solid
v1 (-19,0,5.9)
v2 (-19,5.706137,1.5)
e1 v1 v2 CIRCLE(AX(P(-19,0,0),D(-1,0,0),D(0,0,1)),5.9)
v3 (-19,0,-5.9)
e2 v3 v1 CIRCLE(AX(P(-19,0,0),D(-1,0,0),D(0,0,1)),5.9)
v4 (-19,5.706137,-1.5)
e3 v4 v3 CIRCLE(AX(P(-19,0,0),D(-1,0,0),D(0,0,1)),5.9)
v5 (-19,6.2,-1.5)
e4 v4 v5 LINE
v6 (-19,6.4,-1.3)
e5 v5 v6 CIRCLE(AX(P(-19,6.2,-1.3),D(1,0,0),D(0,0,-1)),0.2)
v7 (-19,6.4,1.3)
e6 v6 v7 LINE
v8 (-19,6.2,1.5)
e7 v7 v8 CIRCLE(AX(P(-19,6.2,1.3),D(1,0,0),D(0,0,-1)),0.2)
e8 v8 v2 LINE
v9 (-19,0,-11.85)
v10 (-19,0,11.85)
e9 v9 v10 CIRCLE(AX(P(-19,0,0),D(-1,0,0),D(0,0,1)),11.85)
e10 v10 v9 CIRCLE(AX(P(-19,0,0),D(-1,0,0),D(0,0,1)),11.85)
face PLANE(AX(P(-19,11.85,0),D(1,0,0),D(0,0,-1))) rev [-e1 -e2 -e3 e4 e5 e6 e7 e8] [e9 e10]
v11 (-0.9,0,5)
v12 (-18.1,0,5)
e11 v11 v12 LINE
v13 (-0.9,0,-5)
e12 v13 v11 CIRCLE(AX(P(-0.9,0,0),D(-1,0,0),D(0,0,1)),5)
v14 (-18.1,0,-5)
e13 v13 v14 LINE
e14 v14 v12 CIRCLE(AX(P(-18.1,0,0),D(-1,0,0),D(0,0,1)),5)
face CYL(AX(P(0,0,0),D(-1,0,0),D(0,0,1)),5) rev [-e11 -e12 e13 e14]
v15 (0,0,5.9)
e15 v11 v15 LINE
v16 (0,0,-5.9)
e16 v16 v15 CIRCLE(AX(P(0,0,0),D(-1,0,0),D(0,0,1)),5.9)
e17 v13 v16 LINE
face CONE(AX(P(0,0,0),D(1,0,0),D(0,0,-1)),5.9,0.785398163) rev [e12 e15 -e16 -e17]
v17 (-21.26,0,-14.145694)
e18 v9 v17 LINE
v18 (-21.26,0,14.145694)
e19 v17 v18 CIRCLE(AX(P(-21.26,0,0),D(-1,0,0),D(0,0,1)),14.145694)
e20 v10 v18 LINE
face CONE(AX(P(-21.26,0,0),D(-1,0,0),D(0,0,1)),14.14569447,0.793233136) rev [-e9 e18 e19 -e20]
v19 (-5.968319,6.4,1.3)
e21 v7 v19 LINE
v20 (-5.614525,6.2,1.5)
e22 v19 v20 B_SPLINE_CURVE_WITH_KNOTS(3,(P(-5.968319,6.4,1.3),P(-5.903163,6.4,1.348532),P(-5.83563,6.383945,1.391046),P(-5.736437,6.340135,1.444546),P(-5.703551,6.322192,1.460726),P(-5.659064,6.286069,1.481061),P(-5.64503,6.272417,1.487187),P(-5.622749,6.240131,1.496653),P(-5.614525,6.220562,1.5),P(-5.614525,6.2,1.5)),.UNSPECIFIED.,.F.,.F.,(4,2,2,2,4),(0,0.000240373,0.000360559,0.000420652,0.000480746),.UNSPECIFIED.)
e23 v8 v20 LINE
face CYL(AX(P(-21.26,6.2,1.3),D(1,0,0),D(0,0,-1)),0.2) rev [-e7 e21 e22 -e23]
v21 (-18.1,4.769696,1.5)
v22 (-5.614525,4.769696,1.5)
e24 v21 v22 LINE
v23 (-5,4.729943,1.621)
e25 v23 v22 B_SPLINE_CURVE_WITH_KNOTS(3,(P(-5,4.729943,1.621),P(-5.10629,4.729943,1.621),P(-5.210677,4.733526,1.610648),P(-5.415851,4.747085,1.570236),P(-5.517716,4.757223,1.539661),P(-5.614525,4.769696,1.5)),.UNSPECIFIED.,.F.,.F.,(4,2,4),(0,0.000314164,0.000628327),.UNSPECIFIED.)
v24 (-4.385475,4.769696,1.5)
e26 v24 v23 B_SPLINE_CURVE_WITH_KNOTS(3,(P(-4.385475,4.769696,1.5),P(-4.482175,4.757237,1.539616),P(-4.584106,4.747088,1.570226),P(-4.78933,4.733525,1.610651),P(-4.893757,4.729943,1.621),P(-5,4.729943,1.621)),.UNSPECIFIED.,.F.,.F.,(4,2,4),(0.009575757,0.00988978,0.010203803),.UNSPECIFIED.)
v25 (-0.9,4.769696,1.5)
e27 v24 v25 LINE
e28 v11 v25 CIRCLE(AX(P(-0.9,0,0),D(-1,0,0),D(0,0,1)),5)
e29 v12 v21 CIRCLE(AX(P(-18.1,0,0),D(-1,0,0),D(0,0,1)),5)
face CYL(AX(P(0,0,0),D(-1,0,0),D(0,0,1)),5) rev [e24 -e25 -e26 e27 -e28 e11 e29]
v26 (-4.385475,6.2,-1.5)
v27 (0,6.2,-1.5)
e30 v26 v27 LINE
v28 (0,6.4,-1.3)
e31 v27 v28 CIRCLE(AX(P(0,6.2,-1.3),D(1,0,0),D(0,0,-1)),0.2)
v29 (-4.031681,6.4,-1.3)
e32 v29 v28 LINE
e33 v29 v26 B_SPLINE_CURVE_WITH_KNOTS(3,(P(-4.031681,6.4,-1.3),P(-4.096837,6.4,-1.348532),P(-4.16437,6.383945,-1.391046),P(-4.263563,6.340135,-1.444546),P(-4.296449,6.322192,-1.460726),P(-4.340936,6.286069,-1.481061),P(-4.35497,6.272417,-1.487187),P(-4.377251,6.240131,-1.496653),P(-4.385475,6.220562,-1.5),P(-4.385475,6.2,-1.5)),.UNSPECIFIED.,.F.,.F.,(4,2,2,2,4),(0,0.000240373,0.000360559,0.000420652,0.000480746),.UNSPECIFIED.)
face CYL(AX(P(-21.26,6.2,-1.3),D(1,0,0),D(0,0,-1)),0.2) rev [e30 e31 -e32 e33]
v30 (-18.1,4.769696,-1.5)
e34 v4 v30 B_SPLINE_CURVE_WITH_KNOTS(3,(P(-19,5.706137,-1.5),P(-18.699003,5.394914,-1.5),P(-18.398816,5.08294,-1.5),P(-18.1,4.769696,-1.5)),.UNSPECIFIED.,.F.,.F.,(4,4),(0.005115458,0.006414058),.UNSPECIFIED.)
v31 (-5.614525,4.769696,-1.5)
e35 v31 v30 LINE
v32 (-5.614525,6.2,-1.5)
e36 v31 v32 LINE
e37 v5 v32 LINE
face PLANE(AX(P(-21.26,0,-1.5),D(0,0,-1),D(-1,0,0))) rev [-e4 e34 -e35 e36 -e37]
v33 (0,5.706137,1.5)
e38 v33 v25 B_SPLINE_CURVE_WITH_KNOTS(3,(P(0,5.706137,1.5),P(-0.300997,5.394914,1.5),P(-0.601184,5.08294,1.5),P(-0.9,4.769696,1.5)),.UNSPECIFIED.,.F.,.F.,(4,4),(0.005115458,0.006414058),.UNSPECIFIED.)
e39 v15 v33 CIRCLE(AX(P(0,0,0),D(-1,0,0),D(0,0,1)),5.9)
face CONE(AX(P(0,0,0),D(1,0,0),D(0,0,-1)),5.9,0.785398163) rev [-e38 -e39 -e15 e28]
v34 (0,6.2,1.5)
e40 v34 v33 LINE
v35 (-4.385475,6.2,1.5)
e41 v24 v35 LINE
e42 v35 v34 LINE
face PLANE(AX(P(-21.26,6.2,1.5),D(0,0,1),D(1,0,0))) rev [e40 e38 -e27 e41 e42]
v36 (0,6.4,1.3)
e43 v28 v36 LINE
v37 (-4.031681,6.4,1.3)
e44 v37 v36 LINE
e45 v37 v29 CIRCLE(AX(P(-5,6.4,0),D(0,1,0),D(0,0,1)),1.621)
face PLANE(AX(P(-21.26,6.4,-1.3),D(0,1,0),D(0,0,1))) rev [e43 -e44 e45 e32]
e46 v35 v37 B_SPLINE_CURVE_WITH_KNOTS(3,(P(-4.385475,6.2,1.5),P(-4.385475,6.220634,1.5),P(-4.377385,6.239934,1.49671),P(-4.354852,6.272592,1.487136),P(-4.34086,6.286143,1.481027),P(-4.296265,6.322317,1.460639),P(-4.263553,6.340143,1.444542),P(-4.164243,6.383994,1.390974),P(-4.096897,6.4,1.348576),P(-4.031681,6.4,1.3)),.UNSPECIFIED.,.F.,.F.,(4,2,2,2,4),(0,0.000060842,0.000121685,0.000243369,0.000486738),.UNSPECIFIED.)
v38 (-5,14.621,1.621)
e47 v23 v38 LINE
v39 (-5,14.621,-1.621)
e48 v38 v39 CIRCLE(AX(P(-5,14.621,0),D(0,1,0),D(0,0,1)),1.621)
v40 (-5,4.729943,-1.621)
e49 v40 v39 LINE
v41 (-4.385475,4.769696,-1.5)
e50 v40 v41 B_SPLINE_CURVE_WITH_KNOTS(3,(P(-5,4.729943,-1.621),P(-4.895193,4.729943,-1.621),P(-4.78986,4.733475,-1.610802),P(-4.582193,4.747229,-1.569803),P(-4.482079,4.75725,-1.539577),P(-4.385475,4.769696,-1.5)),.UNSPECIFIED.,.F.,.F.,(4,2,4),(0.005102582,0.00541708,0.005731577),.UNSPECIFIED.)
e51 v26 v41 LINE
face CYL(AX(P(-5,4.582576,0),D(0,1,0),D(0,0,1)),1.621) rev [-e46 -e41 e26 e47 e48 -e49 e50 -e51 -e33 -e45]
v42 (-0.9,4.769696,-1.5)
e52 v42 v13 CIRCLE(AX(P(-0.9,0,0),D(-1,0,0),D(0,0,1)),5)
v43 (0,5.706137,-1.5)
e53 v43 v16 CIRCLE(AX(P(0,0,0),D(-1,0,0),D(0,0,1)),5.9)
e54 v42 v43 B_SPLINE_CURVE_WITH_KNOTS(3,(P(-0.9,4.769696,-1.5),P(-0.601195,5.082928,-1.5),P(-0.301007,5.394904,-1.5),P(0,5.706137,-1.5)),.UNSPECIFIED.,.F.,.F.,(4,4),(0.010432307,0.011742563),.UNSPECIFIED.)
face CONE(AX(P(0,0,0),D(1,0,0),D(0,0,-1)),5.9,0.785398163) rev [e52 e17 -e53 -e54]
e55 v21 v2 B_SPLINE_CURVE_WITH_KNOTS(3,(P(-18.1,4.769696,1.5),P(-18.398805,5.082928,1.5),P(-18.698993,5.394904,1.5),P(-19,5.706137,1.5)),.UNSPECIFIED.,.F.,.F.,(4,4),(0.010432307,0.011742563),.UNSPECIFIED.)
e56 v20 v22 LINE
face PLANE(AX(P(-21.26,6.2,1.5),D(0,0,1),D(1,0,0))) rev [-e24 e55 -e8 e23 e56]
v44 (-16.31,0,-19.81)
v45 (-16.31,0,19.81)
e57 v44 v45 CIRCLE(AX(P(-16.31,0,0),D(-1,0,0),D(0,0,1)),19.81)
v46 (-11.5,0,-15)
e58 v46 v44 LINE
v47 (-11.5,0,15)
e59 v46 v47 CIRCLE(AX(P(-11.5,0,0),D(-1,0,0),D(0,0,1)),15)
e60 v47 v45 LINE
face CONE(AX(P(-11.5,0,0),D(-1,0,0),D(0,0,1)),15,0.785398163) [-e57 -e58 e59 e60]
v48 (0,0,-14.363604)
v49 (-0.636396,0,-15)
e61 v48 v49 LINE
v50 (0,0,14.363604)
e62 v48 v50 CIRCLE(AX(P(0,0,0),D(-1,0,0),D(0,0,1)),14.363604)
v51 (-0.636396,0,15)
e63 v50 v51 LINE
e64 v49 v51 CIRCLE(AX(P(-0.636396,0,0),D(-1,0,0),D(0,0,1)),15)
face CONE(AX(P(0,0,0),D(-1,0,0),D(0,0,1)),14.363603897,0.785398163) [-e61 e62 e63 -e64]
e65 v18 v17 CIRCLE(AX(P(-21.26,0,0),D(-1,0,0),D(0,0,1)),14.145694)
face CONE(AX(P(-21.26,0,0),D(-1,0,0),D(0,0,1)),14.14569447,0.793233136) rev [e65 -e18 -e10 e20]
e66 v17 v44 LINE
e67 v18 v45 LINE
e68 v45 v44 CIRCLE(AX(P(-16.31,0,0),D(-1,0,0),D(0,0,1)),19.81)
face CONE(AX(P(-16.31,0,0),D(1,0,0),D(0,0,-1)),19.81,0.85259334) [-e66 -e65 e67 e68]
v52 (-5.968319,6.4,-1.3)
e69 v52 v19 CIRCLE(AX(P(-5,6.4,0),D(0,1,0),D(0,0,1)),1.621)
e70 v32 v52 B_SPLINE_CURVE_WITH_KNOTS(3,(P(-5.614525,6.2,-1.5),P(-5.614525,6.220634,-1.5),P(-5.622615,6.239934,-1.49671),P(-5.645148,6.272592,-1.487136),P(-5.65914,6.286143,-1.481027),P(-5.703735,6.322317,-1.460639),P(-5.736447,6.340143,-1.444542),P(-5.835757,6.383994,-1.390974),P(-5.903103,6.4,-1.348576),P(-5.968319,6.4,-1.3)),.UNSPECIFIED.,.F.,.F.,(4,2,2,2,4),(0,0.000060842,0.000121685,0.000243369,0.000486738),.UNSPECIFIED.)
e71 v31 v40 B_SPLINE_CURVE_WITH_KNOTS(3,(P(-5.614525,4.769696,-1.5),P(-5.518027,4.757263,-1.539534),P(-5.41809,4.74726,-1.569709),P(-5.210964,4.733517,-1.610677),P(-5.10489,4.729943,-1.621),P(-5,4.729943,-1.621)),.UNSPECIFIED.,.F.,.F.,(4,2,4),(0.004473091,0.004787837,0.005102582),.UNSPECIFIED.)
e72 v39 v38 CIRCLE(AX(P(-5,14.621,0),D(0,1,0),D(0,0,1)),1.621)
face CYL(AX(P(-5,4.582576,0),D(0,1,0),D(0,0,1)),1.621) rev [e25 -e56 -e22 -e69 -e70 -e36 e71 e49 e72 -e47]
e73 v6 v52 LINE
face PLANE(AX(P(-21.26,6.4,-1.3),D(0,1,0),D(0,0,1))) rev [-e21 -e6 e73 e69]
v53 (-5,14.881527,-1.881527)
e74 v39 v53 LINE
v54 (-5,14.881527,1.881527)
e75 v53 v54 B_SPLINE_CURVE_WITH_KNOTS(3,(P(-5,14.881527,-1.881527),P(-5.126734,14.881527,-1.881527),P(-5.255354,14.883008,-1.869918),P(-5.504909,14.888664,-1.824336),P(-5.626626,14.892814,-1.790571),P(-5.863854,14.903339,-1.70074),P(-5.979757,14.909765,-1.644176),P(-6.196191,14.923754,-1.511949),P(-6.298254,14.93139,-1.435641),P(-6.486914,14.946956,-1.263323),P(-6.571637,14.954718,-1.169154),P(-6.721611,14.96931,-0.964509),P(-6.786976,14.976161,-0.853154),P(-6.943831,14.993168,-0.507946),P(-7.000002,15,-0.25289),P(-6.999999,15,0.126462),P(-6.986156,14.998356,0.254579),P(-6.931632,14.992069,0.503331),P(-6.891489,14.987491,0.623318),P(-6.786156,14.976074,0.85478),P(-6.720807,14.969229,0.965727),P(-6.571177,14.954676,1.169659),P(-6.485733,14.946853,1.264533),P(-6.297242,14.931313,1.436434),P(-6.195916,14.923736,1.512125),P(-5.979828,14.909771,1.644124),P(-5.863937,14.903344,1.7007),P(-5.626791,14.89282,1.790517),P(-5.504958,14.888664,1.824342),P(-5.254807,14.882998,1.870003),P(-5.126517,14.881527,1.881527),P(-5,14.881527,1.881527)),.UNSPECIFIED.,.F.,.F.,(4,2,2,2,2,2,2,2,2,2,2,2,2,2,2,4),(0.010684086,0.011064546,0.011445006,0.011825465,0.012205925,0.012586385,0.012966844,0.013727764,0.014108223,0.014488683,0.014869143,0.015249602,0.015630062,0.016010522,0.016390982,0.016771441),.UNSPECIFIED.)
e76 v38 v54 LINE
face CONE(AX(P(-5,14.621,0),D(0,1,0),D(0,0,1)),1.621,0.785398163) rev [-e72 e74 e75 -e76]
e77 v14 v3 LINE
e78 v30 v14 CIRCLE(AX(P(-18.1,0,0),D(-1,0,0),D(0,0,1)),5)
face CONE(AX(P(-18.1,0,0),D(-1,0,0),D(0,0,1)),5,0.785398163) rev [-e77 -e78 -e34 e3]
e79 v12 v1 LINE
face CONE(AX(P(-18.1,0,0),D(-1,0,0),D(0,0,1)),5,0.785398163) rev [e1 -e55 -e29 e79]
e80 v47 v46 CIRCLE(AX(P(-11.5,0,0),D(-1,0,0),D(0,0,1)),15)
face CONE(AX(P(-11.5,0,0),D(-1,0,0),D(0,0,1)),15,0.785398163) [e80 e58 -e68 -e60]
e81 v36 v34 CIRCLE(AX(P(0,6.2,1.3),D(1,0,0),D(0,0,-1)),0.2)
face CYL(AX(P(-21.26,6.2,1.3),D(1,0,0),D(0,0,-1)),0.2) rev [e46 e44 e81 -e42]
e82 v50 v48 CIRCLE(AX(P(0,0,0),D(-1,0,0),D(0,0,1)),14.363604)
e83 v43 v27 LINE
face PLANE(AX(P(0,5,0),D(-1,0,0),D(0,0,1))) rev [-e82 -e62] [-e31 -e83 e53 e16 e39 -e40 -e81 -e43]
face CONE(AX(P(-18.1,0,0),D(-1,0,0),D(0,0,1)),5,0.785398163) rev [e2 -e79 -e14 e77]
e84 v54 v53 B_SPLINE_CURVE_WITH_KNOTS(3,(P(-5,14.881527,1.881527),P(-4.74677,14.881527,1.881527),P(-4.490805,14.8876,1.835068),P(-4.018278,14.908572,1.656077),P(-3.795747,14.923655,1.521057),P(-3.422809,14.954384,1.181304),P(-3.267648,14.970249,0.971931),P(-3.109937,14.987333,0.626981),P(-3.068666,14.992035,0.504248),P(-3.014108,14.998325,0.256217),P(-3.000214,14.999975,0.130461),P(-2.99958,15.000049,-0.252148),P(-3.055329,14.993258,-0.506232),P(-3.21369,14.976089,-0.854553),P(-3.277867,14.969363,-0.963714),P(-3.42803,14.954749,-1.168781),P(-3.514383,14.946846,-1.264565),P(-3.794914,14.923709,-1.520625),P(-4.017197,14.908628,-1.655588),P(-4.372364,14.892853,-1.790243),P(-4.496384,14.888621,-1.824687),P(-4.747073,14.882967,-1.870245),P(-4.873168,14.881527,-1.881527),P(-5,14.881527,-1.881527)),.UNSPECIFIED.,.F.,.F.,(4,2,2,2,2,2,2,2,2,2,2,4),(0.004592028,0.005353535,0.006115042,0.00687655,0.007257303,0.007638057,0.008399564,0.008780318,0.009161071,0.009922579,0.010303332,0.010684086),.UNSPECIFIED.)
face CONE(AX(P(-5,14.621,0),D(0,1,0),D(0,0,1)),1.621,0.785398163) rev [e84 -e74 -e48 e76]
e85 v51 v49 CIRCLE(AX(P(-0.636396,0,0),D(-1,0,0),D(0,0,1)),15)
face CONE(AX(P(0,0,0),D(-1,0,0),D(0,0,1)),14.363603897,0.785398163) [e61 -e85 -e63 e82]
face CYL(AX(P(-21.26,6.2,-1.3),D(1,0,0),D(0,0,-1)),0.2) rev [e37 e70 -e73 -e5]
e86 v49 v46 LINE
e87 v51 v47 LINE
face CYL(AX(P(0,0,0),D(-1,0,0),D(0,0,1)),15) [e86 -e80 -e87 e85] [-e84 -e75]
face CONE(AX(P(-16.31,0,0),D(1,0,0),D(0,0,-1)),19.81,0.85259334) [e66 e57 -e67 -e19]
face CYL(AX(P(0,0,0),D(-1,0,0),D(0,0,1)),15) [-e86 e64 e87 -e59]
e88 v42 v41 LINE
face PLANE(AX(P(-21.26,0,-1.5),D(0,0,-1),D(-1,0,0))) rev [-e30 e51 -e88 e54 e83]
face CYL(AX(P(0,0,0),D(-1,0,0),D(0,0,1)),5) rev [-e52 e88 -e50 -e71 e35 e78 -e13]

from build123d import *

# Parameters (mm, degrees)
CUT_EXTRUDE_1_DEPTH = 21.26


with BuildPart() as part:
    # 草图1 → 旋转1 (revolve)
    with BuildSketch(Plane.XY, mode=Mode.PRIVATE) as revolve_1_sk:
        Polygon((-21.26, 14.14569447), (-19, 11.85), (-19, 5), (0, 5), (0, 14.363603897), (-0.636396103, 15), (-11.5, 15), (-16.31, 19.81), align=None)
    revolve(revolve_1_sk.sketch.rotate(Axis((0, 0, 0), (-1, 0, 0)), 270), axis=Axis((0, 0, 0), (-1, 0, 0)))

    # 草图2 → 切除-旋转1 (revolve, cut)
    with BuildSketch(Plane.XY, mode=Mode.PRIVATE) as cut_revolve_1_sk:
        Polygon((-19, 0), (-19, 5.9), (-18.1, 5), (-0.9, 5), (0, 5.9), (0, 0), align=None)
    revolve(cut_revolve_1_sk.sketch.rotate(Axis((0, 0, 0), (-1, 0, 0)), 270), axis=Axis((0, 0, 0), (-1, 0, 0)), mode=Mode.SUBTRACT)

    # 草图3 → 切除-旋转2 (revolve, cut)
    with BuildSketch(Plane(origin=(-5, 0, 0), x_dir=(0, 0, -1), z_dir=(1, 0, 0)), mode=Mode.PRIVATE) as cut_revolve_2_sk:
        Polygon((0, 15), (2, 15), (1.621, 14.621), (1.621, 4.582575695), (0, 4.582575695), align=None)
    revolve(cut_revolve_2_sk.sketch.rotate(Axis((-5, 4.582575695, 0), (0, 1, 0)), 180), axis=Axis((-5, 4.582575695, 0), (0, 1, 0)), mode=Mode.SUBTRACT)

    # 草图4 → 切除-拉伸1 (cut)
    with BuildSketch(Plane(origin=(0, 0, 0), x_dir=(0, 0, -1), z_dir=(1, 0, 0))):
        with BuildLine():
            Line((-1.5, 0), (1.5, 0))
            Line((1.5, 0), (1.5, 6.2))
            ThreePointArc((1.5, 6.2), (1.441421356, 6.341421356), (1.3, 6.4))
            Line((1.3, 6.4), (-1.3, 6.4))
            ThreePointArc((-1.3, 6.4), (-1.441421356, 6.341421356), (-1.5, 6.2))
            Line((-1.5, 6.2), (-1.5, 0))
        make_face()
    extrude(amount=-CUT_EXTRUDE_1_DEPTH, mode=Mode.SUBTRACT)


solid = part.part
